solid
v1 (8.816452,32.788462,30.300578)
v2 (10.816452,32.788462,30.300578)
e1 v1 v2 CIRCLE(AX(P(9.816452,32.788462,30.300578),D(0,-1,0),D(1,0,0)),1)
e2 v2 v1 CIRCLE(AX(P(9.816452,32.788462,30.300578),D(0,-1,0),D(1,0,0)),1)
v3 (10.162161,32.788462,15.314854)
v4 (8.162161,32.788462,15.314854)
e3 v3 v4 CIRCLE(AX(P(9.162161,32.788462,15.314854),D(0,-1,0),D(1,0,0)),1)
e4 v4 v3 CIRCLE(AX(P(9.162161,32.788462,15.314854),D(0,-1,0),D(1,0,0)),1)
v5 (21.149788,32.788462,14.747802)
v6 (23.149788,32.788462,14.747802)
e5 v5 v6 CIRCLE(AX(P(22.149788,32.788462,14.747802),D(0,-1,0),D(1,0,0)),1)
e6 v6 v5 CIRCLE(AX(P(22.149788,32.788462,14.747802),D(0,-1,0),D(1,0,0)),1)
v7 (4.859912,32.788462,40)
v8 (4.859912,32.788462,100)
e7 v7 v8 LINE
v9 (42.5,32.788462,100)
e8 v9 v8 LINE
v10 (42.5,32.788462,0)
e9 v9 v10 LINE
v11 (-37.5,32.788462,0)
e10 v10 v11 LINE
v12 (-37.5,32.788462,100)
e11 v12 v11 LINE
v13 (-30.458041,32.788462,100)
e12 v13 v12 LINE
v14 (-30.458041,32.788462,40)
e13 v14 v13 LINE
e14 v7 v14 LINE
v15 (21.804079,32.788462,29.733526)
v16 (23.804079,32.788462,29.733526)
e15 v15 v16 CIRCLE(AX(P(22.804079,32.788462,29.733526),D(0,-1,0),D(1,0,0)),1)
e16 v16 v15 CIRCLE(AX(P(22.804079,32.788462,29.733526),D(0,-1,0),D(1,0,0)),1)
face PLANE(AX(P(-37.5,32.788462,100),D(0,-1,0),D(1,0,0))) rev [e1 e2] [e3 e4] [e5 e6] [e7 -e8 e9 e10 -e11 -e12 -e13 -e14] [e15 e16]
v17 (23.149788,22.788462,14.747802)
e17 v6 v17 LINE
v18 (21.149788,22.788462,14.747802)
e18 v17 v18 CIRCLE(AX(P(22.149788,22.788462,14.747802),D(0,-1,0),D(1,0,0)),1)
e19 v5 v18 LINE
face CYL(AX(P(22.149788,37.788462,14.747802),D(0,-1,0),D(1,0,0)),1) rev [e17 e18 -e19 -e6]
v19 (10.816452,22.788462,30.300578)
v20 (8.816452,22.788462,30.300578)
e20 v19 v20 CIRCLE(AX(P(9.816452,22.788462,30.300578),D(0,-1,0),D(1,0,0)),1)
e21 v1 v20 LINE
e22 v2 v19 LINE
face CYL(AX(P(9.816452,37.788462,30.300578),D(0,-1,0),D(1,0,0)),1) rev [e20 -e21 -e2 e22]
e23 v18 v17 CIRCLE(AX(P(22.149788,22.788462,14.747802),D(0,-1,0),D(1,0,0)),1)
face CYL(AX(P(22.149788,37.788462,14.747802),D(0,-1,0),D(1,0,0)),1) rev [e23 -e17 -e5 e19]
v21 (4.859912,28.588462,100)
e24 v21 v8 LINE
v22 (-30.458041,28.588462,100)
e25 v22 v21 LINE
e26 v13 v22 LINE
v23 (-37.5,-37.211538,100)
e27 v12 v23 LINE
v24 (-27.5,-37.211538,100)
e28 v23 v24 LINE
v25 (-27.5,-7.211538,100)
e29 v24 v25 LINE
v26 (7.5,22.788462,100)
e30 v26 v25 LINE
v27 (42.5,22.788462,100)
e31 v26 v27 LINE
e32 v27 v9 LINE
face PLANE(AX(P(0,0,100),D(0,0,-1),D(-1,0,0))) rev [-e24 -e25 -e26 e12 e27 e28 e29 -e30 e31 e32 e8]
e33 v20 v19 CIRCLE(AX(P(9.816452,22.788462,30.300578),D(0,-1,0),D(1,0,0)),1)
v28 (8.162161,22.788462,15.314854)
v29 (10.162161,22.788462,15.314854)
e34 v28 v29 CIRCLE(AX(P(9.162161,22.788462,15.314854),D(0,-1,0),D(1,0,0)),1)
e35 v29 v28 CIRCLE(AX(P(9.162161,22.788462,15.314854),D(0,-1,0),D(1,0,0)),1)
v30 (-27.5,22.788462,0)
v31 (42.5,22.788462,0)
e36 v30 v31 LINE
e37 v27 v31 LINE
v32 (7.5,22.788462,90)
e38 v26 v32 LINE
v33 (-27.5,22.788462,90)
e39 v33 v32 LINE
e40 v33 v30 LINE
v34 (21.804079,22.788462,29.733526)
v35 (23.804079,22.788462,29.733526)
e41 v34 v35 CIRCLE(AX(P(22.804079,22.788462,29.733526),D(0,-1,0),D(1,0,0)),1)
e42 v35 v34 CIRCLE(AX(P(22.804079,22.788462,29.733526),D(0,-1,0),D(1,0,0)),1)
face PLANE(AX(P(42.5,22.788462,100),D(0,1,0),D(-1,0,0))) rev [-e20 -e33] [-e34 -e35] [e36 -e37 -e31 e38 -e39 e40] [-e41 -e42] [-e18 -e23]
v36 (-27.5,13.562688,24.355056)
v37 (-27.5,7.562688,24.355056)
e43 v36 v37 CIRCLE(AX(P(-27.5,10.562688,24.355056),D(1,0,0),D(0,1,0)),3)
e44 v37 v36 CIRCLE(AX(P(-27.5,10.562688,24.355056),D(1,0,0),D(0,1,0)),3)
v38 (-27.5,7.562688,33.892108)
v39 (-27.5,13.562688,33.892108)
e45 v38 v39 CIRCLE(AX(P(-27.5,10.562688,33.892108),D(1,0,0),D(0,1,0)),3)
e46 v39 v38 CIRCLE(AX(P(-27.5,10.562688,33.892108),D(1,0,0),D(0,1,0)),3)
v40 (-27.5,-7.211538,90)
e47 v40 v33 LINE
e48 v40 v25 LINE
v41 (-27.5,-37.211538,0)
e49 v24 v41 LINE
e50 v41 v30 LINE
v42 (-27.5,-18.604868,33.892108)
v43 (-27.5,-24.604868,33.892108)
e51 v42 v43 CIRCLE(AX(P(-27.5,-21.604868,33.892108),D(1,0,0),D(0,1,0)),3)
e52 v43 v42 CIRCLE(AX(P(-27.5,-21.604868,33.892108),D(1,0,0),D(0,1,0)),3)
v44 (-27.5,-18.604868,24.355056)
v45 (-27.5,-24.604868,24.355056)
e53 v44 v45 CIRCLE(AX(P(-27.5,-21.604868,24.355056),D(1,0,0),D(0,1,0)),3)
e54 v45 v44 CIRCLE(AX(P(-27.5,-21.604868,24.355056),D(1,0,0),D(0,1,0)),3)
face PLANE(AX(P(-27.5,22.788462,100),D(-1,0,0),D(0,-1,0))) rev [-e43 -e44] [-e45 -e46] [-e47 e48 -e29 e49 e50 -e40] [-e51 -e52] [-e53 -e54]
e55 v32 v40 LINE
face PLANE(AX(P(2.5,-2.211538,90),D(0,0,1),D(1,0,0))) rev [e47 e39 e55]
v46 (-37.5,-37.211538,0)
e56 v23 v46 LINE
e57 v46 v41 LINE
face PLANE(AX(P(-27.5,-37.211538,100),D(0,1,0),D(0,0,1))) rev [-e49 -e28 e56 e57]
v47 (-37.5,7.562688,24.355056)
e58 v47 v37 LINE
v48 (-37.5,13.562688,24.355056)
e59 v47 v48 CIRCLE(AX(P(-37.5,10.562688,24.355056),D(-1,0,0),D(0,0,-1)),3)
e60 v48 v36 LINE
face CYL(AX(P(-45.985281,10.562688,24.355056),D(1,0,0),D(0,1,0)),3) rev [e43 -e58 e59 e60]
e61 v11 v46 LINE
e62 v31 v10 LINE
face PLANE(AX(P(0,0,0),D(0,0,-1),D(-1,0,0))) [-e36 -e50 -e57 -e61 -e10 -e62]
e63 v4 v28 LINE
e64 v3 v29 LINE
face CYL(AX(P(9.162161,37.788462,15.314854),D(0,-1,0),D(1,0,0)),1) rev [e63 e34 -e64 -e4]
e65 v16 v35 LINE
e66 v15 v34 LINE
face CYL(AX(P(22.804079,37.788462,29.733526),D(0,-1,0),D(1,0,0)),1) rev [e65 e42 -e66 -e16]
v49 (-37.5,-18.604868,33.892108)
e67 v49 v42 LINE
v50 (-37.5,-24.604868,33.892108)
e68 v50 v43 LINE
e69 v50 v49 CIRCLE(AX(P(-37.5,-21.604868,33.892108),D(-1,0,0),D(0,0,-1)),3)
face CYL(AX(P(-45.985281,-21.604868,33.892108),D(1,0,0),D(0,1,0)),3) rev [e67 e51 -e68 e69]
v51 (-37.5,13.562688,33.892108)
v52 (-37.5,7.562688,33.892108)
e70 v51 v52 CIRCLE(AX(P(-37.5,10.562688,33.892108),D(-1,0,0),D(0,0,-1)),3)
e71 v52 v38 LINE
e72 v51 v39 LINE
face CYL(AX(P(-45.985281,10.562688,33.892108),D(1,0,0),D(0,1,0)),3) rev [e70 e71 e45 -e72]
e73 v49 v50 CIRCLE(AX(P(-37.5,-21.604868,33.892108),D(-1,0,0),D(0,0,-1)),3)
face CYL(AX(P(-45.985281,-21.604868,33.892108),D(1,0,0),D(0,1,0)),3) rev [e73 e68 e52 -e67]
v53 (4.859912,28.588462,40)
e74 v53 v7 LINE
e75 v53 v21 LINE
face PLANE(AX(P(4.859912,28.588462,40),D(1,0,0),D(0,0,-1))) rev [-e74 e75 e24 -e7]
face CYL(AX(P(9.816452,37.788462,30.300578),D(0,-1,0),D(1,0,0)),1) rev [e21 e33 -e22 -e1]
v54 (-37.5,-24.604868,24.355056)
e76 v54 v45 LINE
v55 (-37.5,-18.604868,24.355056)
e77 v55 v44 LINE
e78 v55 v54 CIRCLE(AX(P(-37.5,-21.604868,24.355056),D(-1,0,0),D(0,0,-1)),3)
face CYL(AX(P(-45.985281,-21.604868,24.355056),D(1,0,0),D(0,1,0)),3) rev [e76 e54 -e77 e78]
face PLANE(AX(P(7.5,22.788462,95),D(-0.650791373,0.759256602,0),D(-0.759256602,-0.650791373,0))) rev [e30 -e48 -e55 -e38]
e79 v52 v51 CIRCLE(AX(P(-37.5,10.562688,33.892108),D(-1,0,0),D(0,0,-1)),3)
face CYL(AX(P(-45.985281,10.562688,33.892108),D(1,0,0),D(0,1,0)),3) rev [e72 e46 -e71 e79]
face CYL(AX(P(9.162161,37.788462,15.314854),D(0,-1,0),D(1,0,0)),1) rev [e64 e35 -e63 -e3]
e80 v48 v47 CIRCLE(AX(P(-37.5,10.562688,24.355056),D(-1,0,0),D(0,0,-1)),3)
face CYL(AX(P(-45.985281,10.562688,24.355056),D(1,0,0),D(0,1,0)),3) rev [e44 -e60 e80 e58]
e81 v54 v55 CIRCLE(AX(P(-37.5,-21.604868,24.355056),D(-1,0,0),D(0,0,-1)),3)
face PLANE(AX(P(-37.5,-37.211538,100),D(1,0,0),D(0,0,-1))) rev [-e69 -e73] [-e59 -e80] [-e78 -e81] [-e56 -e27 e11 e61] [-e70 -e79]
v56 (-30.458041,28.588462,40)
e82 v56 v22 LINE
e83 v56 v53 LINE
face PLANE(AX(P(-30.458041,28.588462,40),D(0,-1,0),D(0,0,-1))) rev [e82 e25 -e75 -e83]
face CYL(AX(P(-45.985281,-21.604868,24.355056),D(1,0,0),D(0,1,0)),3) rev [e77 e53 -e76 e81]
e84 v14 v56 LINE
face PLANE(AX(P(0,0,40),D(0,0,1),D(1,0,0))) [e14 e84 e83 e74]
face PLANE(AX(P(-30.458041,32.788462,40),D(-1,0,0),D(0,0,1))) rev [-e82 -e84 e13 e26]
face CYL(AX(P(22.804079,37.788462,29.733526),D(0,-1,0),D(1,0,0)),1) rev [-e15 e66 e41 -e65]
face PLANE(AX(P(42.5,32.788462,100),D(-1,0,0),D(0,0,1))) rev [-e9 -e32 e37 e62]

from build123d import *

# Parameters (mm, degrees)
EXTRUDE_1_DEPTH     = 100
SKETCH_2_W          = 35.317953013
SKETCH_2_H          = 4.2
CUT_EXTRUDE_1_DEPTH = 60
RIB_6_REACH         = 112.526
SKETCH_5_WALL_W     = 269.149287264
SKETCH_5_WALL_H     = 10
SKETCH_6_R          = 3
CUT_EXTRUDE_2_DEPTH = 10
SKETCH_7_R          = 1
CUT_EXTRUDE_3_DEPTH = 15


with BuildPart() as part:
    # 草图1 → 凸台-拉伸1 (new body)
    with BuildSketch(Plane.XY):
        Polygon((-37.5, 32.788461538), (42.5, 32.788461538), (42.5, 22.788461538), (-27.5, 22.788461538), (-27.5, -37.211538462), (-37.5, -37.211538462), align=None)
    extrude(amount=EXTRUDE_1_DEPTH)

    # 草图2 → 切除-拉伸1 (cut)
    with BuildSketch(Plane.XY.offset(100)):
        with Locations((-12.799064643, 30.688461538)):
            Rectangle(SKETCH_2_W, SKETCH_2_H)
    extrude(amount=-CUT_EXTRUDE_1_DEPTH, mode=Mode.SUBTRACT)

    # 草图5 wall → 筋6 (add, up to next)
    with BuildSketch(Plane(origin=(-10, 7.788461538, 95), x_dir=(-0.759256602365, -0.650791373456, 0), z_dir=(0.650791373456, -0.759256602365, 0)), mode=Mode.PRIVATE) as rib_6_sk1:
        Rectangle(SKETCH_5_WALL_W, SKETCH_5_WALL_H)
    rib_6_tool1 = extrude(rib_6_sk1.sketch, amount=-RIB_6_REACH, mode=Mode.PRIVATE) - part.part
    add(rib_6_tool1.solids().sort_by_distance((-10, 7.788461538, 95))[0])

    # 草图6 → 切除-拉伸2 (cut)
    with BuildSketch(Plane(origin=(-27.5, 891.532711259, -866.3577183), x_dir=(0, 0, 1), z_dir=(1, 0, 0))):
        with Locations(Location((900.249826396, 880.97002325, 0), (0, 0, 270))):
            Circle(SKETCH_6_R)
        with Locations(Location((890.712774703, 880.97002325, 0), (0, 0, 270))):
            Circle(SKETCH_6_R)
        with Locations(Location((900.249826396, 913.137579673, 0), (0, 0, 270))):
            Circle(SKETCH_6_R)
        with Locations(Location((890.712774703, 913.137579673, 0), (0, 0, 270))):
            Circle(SKETCH_6_R)
    extrude(amount=-CUT_EXTRUDE_2_DEPTH, mode=Mode.SUBTRACT)

    # 草图7 → 切除-拉伸3 (cut)
    with BuildSketch(Plane(origin=(1081.455900364, 22.788461538, -866.3577183), x_dir=(-0.07845909572783148, 0, 0.9969173337331291), z_dir=(0, -1, 0))):
        with Locations(Location((963.085867609, 999.8129825, 0), (0, 0, 265.5))):
            Circle(SKETCH_7_R)
        with Locations(Location((977.974059883, 997.984942349, 0), (0, 0, 265.5))):
            Circle(SKETCH_7_R)
        with Locations(Location((961.501566145, 986.909882529, 0), (0, 0, 265.5))):
            Circle(SKETCH_7_R)
        with Locations(Location((976.389758419, 985.081842378, 0), (0, 0, 265.5))):
            Circle(SKETCH_7_R)
    extrude(amount=-CUT_EXTRUDE_3_DEPTH, mode=Mode.SUBTRACT)


solid = part.part
